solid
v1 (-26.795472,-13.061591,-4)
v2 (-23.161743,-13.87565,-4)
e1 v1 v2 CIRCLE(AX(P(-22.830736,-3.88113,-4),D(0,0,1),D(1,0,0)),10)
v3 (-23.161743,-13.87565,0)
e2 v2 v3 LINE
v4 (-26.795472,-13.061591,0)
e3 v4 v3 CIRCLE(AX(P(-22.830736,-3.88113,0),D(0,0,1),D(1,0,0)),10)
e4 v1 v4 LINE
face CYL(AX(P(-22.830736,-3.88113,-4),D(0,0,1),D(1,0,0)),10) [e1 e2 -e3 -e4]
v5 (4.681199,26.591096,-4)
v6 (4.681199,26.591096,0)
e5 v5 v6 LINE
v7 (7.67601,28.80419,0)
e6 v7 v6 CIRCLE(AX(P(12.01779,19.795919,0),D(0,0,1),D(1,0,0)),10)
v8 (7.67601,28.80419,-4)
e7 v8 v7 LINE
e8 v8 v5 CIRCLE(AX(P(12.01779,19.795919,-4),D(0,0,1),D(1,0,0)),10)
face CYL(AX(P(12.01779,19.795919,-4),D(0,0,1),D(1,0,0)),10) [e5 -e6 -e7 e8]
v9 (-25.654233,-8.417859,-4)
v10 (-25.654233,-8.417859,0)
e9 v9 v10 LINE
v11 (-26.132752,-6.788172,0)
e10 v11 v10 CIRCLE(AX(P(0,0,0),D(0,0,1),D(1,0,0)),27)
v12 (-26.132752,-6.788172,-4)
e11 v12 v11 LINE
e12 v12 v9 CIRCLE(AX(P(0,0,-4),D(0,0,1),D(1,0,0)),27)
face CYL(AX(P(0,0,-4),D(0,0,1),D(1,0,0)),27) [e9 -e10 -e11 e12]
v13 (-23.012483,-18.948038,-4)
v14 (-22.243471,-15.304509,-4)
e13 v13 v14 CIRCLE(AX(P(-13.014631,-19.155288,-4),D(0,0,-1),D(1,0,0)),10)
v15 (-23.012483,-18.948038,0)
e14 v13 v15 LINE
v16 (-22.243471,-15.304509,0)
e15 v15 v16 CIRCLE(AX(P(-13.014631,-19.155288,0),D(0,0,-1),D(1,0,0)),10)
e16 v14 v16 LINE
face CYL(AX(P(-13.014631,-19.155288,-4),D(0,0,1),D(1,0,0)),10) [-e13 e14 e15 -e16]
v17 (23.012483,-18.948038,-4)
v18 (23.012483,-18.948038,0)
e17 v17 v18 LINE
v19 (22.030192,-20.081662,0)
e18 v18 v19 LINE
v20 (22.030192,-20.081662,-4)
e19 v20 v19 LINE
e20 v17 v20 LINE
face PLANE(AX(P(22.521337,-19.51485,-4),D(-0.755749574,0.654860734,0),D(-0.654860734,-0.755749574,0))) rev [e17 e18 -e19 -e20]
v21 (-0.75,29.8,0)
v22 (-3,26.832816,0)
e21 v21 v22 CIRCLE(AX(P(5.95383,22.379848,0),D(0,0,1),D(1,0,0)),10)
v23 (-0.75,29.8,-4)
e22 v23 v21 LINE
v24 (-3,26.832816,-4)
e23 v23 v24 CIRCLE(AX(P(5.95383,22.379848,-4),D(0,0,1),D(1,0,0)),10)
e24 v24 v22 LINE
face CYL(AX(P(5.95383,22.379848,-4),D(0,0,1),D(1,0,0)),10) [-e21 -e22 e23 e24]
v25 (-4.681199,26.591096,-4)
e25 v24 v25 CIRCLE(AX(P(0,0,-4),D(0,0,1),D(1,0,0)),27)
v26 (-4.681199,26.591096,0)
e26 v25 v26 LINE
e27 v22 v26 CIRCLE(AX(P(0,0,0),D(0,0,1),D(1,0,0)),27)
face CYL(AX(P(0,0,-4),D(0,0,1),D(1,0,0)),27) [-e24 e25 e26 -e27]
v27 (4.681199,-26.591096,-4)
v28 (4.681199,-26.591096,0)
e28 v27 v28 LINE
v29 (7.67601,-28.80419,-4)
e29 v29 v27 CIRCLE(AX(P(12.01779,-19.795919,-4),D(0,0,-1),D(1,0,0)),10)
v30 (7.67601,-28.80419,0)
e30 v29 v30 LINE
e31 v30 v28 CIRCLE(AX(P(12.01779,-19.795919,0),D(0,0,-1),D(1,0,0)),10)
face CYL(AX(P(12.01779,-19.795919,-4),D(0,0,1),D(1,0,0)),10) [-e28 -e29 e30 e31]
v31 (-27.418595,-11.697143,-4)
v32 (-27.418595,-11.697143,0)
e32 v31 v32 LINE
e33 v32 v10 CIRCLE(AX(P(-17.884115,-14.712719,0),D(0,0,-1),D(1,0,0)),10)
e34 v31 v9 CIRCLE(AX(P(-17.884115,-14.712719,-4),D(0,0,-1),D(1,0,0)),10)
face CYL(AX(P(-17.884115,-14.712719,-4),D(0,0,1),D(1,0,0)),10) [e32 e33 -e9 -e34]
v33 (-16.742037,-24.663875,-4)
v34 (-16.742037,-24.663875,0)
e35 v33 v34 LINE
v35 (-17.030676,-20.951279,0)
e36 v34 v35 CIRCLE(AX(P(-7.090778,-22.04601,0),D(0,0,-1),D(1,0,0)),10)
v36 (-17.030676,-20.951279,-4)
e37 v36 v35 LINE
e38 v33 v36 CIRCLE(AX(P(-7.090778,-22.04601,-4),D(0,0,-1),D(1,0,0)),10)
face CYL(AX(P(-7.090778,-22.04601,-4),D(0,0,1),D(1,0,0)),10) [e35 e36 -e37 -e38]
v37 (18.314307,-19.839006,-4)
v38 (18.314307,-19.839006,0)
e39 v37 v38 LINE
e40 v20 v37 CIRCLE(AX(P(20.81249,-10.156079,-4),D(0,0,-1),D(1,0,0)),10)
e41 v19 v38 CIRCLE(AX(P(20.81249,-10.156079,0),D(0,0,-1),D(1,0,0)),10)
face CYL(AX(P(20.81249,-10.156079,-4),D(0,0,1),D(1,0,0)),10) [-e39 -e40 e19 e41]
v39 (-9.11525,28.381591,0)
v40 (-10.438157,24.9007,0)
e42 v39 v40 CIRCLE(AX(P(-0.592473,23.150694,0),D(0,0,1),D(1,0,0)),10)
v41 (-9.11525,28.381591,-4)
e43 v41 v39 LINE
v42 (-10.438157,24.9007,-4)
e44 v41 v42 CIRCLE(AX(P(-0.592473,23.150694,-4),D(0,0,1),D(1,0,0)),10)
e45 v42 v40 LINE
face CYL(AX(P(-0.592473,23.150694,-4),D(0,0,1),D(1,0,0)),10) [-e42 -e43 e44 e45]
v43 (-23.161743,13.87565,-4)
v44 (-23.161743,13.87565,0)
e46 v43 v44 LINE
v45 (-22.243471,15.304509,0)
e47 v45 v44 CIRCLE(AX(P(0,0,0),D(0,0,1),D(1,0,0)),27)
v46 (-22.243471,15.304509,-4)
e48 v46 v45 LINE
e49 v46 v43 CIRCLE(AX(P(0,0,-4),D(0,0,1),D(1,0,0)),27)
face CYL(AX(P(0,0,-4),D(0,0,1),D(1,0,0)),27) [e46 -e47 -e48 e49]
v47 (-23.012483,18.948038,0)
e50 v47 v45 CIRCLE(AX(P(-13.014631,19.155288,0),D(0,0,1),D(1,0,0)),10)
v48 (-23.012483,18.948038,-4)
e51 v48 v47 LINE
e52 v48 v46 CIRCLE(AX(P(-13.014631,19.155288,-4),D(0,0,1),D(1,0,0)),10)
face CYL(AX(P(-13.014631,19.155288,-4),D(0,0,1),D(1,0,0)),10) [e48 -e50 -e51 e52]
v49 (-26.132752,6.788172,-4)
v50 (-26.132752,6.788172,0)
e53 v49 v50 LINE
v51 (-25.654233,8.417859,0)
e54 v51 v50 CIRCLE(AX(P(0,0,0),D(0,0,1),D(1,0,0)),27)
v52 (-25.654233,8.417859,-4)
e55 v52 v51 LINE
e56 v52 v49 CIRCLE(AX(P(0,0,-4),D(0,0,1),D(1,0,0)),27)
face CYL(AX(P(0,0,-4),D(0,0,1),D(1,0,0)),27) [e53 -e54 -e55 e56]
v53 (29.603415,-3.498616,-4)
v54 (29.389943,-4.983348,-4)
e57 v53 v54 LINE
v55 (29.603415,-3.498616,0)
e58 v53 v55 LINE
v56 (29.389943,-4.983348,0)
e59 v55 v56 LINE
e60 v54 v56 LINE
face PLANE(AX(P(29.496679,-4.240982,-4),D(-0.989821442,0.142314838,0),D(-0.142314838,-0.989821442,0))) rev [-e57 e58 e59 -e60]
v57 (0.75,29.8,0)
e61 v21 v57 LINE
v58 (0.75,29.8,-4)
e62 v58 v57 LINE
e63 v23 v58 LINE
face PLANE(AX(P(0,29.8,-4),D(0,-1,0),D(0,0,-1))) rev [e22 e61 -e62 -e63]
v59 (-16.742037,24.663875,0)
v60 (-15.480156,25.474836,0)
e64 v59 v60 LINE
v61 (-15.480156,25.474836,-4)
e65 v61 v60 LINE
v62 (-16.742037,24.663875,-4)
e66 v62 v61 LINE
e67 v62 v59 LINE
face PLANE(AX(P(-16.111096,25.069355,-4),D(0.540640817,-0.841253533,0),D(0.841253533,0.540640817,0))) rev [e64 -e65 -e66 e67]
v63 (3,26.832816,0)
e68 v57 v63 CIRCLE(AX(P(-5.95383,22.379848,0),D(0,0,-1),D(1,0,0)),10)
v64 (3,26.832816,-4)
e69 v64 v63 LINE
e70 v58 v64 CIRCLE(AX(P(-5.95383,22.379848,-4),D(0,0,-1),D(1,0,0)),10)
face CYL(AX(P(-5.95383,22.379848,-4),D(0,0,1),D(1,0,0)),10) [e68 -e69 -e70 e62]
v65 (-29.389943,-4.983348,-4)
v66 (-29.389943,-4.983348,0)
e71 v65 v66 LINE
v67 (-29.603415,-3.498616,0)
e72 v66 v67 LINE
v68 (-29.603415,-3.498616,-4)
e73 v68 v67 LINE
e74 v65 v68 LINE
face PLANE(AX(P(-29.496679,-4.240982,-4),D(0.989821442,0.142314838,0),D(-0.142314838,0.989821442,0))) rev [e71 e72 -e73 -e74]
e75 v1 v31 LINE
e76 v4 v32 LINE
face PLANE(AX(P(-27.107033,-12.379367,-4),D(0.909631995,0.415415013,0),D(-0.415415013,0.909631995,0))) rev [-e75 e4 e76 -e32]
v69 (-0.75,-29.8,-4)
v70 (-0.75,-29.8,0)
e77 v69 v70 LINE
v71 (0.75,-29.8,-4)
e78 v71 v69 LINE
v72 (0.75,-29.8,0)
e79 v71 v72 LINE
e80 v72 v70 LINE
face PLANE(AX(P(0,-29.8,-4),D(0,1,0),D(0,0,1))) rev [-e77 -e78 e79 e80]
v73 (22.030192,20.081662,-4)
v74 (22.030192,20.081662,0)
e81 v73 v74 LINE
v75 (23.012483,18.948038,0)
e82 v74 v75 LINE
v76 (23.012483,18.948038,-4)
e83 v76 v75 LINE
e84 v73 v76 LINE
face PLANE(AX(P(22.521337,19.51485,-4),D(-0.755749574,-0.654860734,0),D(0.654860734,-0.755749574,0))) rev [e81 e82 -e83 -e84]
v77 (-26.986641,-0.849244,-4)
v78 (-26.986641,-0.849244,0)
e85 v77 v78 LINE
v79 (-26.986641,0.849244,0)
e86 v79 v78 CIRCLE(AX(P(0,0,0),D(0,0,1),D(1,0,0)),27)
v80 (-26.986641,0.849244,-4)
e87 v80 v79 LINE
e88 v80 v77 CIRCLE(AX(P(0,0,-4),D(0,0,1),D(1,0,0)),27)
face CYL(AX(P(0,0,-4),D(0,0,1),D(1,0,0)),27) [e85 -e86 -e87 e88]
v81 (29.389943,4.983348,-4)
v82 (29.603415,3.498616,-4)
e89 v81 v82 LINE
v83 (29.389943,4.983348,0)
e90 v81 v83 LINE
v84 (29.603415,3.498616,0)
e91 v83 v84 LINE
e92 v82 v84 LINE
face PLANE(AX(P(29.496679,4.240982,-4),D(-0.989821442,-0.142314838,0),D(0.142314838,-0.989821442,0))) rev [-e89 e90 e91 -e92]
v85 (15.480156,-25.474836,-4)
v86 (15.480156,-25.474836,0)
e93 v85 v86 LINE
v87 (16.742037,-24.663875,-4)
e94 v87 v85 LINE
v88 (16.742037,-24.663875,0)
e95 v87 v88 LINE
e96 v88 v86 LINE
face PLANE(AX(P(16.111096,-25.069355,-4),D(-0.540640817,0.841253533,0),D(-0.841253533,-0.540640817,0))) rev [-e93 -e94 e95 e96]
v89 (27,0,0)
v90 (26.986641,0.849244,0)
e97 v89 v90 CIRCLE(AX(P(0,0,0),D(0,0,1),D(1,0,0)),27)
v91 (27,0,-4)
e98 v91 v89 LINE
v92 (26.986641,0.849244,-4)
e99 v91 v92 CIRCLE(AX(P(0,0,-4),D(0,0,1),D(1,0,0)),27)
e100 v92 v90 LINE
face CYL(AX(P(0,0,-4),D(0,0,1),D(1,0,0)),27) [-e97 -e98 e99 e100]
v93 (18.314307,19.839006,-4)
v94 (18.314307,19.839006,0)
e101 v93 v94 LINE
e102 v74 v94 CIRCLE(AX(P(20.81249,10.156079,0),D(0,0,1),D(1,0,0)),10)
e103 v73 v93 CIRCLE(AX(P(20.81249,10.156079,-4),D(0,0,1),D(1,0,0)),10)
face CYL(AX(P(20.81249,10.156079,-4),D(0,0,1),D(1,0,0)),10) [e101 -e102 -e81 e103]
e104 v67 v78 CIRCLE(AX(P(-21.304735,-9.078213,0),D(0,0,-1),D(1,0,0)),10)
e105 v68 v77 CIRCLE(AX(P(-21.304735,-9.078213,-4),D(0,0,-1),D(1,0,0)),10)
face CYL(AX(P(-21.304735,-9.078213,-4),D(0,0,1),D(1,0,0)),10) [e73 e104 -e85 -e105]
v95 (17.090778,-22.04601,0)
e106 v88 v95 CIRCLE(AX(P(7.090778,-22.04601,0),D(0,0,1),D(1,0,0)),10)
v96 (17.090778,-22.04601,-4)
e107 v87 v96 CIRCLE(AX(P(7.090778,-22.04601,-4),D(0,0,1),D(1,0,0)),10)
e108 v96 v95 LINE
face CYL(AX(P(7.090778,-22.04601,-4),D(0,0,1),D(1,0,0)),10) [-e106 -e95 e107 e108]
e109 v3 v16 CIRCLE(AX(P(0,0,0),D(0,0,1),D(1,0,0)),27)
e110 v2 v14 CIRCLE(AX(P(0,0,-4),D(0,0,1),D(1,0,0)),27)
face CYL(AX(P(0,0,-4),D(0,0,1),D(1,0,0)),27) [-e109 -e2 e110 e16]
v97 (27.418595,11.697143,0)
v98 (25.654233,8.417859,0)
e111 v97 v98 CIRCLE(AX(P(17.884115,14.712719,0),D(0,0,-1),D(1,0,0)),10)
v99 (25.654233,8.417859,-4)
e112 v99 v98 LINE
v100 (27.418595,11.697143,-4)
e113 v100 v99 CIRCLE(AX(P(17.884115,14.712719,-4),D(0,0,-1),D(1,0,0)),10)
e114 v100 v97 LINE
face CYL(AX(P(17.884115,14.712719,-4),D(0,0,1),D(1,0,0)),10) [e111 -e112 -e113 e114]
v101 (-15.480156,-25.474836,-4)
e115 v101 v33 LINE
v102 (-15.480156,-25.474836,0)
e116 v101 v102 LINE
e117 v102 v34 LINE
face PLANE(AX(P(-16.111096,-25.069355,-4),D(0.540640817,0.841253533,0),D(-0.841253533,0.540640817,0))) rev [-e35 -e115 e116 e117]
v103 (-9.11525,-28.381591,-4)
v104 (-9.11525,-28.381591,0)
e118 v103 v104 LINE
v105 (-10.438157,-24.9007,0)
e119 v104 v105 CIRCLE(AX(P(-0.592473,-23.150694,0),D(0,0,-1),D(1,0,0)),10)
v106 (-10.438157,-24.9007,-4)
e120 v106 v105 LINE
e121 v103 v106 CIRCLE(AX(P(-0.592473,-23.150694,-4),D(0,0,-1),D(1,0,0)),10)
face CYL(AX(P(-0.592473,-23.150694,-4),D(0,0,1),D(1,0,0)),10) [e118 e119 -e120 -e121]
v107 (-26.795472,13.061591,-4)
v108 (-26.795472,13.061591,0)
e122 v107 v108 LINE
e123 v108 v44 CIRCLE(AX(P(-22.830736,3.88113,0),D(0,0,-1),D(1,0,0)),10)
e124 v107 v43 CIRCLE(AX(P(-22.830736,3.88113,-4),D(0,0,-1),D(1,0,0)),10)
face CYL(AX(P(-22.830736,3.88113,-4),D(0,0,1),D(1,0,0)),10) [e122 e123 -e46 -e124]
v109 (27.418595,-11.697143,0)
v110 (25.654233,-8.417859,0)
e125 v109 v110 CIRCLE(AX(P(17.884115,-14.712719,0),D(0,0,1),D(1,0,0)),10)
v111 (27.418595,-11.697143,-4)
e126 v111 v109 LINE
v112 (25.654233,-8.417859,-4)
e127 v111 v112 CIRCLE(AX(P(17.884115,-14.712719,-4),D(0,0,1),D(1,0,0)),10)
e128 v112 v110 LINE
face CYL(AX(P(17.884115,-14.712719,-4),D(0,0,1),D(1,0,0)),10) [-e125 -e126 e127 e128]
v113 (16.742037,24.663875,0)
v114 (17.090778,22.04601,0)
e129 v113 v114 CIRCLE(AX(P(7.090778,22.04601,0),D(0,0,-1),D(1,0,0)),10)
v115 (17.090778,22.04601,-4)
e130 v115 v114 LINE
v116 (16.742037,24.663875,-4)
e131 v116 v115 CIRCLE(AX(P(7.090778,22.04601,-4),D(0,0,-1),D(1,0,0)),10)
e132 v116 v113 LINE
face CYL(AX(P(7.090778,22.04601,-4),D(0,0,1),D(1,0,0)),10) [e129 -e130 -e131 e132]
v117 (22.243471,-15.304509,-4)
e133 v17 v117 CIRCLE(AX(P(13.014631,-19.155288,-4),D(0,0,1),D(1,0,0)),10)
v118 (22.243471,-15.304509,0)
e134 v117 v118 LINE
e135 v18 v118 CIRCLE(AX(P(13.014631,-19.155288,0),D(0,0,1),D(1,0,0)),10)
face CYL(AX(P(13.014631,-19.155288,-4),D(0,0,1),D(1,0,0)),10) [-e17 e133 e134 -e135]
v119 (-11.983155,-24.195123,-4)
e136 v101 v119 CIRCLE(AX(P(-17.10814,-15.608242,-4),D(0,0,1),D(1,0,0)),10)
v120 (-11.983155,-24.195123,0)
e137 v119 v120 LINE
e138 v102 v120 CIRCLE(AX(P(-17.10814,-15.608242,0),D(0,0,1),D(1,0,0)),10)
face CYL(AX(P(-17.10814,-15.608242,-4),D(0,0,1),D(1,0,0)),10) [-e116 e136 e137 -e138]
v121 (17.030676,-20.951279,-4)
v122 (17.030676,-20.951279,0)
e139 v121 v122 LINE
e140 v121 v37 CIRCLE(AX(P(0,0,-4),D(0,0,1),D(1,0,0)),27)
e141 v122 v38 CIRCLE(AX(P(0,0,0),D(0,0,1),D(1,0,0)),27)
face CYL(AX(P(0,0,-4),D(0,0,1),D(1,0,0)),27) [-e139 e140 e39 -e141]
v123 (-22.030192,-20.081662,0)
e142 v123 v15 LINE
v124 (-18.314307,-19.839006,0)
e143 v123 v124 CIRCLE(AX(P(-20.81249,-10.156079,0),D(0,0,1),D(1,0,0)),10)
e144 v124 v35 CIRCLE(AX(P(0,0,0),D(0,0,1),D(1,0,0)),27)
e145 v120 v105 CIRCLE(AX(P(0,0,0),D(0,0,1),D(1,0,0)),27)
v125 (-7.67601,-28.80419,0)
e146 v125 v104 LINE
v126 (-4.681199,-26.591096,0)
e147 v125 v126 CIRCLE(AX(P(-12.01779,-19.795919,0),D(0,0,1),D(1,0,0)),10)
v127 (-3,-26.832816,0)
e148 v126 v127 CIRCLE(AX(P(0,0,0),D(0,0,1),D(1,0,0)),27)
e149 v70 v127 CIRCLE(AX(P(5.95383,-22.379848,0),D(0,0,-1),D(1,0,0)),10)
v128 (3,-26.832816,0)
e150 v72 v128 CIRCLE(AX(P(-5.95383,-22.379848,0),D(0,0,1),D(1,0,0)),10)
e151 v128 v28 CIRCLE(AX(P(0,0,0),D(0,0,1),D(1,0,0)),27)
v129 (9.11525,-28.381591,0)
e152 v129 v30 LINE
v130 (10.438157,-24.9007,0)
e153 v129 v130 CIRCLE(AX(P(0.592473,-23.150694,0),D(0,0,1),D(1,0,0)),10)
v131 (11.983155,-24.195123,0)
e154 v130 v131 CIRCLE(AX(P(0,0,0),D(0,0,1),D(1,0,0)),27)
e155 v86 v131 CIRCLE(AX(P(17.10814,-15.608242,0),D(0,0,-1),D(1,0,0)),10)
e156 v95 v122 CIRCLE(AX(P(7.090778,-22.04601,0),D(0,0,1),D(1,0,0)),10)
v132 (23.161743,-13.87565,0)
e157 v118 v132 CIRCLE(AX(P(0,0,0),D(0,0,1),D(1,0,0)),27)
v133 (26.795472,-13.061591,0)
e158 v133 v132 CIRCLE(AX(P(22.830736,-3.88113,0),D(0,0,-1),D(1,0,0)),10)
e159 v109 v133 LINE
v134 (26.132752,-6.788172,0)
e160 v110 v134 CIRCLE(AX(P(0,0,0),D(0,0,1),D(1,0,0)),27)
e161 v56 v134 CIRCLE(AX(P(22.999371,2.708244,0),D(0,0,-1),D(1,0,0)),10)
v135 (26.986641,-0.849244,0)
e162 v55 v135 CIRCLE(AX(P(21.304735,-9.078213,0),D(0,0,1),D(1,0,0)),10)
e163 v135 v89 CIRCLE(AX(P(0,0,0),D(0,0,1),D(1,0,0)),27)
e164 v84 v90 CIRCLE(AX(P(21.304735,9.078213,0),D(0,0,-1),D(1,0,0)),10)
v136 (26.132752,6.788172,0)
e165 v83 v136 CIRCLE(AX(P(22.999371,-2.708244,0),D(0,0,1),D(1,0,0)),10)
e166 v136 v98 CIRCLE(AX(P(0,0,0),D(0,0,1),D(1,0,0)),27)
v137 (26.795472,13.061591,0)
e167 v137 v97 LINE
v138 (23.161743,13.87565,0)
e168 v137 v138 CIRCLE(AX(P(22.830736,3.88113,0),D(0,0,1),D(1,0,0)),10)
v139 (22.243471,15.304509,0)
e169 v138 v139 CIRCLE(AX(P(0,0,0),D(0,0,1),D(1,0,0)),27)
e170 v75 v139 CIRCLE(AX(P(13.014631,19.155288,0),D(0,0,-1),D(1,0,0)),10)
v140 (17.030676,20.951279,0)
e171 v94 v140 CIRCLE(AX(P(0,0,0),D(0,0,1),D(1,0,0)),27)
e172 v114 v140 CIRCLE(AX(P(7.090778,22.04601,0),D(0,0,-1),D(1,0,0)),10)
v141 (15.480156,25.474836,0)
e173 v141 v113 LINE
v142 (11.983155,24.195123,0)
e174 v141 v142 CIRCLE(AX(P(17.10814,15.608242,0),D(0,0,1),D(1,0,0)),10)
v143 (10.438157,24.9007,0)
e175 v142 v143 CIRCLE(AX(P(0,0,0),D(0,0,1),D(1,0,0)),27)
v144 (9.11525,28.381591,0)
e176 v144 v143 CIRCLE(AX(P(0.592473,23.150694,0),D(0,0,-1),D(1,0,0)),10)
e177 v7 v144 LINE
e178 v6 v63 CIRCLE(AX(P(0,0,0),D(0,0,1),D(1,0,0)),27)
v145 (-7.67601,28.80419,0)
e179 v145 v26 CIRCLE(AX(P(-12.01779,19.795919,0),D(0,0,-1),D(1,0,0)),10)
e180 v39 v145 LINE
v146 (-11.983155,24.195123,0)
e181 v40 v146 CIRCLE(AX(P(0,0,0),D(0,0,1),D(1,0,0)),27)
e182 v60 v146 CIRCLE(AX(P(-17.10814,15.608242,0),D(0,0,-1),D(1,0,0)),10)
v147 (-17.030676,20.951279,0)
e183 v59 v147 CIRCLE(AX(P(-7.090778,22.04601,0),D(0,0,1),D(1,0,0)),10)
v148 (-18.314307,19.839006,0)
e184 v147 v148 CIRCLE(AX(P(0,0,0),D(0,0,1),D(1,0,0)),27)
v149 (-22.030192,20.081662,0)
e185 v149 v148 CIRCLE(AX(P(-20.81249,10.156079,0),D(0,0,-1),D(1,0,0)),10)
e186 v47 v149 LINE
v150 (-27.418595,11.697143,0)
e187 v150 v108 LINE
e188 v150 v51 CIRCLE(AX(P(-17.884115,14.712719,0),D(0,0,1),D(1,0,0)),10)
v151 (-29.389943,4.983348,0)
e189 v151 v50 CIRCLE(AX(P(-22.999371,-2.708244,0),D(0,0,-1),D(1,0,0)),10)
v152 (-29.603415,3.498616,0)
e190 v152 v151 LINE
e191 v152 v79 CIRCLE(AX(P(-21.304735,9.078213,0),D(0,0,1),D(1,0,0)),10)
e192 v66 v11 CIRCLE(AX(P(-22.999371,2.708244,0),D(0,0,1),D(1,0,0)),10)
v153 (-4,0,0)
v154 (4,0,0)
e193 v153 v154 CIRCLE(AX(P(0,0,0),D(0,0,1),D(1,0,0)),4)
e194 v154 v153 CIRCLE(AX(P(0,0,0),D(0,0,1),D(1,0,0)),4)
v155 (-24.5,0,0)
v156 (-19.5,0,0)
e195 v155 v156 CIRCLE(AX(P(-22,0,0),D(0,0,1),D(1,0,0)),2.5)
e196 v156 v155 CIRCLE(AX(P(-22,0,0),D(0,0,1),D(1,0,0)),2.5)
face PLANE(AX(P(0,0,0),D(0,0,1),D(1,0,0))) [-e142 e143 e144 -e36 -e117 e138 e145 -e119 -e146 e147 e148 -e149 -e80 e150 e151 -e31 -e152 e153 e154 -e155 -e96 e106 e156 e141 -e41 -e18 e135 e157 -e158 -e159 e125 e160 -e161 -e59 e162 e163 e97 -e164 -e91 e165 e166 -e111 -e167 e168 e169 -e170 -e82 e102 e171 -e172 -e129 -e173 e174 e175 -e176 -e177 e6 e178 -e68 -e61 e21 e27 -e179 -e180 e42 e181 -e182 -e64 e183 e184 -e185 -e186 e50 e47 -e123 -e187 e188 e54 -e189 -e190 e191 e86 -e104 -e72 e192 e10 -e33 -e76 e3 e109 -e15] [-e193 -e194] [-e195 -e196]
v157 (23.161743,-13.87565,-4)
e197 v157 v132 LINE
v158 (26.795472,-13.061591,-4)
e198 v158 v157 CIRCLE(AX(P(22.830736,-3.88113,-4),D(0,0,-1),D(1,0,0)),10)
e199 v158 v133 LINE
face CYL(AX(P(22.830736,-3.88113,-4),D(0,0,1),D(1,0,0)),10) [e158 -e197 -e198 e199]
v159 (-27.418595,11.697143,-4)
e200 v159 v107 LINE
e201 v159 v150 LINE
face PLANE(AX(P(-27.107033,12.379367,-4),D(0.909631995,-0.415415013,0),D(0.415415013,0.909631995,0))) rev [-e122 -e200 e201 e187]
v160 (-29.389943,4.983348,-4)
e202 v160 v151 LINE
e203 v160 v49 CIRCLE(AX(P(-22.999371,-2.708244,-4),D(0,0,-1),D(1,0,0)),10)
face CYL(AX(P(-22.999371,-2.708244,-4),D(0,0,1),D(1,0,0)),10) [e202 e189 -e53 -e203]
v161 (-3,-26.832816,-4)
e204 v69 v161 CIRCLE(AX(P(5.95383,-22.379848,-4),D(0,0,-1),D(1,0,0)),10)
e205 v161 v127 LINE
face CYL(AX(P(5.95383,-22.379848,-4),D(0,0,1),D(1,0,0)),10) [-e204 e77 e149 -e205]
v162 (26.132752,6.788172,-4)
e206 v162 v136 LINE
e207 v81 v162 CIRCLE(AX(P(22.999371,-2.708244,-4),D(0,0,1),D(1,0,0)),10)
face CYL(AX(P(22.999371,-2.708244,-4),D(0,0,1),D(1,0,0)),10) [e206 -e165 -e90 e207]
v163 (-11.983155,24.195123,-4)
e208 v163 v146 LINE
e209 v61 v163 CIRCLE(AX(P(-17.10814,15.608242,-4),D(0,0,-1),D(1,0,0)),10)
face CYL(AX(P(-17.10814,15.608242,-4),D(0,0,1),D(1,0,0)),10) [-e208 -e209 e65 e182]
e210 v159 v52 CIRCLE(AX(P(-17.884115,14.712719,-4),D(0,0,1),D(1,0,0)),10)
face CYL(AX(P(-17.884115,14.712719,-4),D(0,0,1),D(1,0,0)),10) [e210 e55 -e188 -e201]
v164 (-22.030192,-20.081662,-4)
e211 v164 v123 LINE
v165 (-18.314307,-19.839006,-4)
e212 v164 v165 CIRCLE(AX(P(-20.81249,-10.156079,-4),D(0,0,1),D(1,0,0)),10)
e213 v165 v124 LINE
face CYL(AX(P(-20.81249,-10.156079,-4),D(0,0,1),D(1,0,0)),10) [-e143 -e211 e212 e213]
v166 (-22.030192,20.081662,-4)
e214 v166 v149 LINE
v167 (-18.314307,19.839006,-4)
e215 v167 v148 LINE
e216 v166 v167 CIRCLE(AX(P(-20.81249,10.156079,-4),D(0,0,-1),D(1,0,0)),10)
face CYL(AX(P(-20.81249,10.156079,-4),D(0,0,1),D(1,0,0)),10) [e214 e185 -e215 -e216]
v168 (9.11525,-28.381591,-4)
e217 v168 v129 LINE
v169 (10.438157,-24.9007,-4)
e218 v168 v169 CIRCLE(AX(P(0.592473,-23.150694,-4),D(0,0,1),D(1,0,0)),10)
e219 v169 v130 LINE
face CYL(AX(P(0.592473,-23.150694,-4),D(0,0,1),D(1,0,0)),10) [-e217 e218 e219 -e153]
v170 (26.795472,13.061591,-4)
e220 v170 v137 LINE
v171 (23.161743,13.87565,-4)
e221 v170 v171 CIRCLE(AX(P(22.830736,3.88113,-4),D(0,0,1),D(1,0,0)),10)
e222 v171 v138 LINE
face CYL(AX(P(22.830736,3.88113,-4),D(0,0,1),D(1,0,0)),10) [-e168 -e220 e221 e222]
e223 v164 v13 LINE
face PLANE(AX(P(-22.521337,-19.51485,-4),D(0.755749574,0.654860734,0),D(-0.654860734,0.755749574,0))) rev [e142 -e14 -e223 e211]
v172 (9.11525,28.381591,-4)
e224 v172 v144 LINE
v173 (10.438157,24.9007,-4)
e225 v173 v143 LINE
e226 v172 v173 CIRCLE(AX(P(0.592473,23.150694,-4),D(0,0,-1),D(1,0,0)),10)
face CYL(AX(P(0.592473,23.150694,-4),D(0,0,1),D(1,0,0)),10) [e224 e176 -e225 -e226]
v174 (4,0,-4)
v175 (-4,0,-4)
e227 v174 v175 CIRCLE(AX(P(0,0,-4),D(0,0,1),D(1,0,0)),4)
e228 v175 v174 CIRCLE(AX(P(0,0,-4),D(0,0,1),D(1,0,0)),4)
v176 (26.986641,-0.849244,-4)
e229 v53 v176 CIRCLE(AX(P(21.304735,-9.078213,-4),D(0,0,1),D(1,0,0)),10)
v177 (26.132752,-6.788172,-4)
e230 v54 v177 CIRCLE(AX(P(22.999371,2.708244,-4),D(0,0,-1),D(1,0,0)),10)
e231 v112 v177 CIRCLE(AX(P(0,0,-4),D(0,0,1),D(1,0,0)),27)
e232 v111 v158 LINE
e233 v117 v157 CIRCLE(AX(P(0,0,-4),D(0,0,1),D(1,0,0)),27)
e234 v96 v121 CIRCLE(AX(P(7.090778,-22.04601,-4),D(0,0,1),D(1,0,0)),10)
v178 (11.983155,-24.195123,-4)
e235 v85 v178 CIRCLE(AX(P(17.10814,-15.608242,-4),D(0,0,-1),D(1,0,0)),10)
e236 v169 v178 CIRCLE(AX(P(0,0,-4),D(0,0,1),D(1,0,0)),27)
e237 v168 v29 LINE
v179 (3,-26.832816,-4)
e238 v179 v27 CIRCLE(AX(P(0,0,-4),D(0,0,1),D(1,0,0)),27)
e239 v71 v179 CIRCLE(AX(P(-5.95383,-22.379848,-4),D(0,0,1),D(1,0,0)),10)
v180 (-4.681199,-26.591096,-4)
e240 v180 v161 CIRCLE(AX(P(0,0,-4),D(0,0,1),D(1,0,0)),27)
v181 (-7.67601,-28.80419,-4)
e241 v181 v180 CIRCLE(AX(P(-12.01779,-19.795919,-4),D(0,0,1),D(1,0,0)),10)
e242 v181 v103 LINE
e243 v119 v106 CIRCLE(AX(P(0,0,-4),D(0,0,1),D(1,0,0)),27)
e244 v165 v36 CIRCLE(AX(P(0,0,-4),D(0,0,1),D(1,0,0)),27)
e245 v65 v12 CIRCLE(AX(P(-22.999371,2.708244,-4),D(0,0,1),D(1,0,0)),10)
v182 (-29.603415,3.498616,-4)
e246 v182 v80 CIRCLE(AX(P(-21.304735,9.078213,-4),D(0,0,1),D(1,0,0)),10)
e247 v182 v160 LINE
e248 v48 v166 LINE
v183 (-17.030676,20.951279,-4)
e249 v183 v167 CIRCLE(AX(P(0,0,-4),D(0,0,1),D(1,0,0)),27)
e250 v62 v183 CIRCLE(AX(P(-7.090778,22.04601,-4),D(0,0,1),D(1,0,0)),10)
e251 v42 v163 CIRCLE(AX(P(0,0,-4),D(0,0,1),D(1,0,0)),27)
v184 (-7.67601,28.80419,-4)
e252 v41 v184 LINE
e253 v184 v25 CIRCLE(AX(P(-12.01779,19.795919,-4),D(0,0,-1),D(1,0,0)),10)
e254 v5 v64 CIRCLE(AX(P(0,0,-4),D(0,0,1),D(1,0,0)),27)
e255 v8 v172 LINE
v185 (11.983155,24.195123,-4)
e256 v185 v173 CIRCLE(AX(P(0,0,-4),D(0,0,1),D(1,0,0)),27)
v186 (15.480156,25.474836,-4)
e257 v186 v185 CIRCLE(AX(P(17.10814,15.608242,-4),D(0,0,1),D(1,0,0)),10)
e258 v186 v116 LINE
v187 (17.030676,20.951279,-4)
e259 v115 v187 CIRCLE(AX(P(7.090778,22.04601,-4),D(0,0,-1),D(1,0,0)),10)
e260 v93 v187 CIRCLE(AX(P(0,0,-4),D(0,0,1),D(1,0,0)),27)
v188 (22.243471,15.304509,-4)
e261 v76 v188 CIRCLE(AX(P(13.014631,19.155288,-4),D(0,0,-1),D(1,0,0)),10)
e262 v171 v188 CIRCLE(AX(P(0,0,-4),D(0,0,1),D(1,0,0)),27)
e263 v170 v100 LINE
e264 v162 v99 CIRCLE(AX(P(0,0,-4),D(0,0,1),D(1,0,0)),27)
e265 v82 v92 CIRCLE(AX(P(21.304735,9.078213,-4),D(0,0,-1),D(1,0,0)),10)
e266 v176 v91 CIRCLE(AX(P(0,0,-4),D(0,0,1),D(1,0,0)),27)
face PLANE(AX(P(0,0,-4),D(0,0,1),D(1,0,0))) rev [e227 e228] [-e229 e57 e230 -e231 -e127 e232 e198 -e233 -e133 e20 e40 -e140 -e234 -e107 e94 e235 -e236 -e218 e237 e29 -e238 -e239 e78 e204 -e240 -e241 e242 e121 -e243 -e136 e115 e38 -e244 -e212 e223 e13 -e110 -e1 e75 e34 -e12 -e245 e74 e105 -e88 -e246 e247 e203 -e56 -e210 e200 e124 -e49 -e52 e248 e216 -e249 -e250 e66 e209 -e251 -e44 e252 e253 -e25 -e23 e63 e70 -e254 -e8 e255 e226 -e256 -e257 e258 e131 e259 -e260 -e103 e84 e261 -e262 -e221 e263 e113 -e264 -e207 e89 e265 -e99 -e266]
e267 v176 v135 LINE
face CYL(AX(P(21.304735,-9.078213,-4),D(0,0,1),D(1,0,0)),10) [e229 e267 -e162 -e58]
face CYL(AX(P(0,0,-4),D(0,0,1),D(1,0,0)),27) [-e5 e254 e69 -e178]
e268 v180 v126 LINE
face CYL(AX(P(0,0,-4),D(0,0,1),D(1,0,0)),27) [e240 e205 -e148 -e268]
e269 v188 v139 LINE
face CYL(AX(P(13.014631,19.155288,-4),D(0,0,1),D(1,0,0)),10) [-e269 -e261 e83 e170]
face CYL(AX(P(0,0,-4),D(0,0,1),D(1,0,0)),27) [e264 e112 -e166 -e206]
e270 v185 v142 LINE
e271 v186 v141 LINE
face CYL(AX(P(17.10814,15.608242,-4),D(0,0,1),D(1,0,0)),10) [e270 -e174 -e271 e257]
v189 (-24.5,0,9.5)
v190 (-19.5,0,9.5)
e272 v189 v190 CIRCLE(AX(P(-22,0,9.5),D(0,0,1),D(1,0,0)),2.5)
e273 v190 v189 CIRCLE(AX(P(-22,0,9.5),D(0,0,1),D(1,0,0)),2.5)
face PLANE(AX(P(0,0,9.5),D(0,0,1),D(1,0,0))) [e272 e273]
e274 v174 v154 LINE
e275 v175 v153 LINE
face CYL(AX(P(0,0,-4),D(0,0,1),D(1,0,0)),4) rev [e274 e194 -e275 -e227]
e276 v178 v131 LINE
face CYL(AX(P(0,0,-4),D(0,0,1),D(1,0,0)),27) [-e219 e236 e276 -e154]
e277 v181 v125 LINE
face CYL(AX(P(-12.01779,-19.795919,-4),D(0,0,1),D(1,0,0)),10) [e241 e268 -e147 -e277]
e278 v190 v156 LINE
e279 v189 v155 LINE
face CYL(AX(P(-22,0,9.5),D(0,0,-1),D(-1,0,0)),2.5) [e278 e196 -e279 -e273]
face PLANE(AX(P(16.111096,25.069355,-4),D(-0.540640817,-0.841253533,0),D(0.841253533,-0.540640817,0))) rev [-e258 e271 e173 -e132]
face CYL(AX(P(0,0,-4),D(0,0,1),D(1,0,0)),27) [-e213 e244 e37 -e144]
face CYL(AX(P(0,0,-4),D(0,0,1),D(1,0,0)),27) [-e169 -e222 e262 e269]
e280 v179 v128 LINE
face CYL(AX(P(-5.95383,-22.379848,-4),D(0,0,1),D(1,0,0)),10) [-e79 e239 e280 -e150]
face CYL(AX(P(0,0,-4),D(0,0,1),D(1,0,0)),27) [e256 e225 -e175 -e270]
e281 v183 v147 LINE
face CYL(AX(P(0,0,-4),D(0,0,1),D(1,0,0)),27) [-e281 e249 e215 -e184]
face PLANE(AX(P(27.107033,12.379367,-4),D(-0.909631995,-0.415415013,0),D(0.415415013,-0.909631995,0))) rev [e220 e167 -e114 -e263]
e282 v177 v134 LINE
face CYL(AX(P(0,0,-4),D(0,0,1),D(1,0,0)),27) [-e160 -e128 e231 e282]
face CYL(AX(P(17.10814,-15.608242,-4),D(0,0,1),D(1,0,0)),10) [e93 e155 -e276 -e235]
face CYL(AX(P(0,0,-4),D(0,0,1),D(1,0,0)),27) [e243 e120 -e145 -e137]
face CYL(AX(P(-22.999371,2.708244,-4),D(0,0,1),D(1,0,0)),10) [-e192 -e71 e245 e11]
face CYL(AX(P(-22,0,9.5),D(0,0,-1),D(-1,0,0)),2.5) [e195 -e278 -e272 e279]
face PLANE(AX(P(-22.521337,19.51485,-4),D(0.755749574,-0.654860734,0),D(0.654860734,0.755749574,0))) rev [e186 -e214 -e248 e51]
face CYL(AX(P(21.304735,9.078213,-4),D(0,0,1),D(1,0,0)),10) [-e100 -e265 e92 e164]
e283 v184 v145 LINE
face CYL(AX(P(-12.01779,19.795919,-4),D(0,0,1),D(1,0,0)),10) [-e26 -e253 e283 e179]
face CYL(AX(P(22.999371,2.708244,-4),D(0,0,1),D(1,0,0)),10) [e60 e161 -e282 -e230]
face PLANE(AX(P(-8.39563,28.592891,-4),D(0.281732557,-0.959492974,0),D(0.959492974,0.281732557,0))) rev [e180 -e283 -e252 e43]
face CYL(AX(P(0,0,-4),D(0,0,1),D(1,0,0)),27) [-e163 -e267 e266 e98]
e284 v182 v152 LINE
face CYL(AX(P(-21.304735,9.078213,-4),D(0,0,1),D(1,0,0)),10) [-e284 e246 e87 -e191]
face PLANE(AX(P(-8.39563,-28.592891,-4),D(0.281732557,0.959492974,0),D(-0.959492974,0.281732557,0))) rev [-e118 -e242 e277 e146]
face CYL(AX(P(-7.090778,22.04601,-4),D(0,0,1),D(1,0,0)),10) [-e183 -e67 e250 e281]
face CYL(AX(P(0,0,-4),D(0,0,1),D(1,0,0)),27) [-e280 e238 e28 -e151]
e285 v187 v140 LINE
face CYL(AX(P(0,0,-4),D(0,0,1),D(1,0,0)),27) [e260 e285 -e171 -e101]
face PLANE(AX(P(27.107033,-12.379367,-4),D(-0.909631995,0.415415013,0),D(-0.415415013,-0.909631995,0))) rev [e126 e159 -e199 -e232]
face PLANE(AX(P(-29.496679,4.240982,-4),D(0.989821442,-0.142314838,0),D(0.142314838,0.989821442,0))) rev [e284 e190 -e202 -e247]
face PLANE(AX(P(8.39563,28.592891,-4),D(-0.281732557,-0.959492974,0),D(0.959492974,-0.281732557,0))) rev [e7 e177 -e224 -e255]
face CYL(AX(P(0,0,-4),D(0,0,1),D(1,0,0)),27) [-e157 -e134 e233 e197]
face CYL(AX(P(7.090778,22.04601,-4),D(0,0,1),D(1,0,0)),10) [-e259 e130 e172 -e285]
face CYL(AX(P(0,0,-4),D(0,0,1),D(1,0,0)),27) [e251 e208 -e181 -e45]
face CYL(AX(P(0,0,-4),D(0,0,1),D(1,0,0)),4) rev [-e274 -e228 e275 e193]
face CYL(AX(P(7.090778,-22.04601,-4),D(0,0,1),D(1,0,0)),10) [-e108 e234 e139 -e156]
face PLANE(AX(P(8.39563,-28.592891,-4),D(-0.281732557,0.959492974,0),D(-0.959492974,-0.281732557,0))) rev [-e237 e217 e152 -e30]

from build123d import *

# Parameters (mm, degrees)
GEAR_PROFILE_SKETCH_R = 4
GEAR_BODY_22T_DEPTH   = 4
SKETCH1_3_R           = 2.5
HUB_BOSS_DEPTH        = 9.5


with BuildPart() as part:
    # Gear Profile Sketch → Gear Body 22T (new body)
    with BuildSketch(Plane.XY):
        with BuildLine():
            Line((-0.75, 29.8), (0.75, 29.8))
            ThreePointArc((0.75, 29.8), (2.014333197, 28.422063485), (3, 26.83281573))
            ThreePointArc((3, 26.83281573), (3.842500633, 26.725178931), (4.681198862, 26.591095826))
            ThreePointArc((4.681198862, 26.591095826), (6.074682067, 27.838273451), (7.676010464, 28.804190031))
            Line((7.676010464, 28.804190031), (9.115249924, 28.381591196))
            ThreePointArc((9.115249924, 28.381591196), (9.940159165, 26.703266967), (10.438156704, 24.900700485))
            ThreePointArc((10.438156704, 24.900700485), (11.216205351, 24.560063875), (11.983154832, 24.195123481))
            ThreePointArc((11.983154832, 24.195123481), (13.671562718, 24.999192063), (15.480156211, 25.474835891))
            Line((15.480156211, 25.474835891), (16.74203651, 24.663874665))
            ThreePointArc((16.74203651, 24.663874665), (17.060692554, 22.821130571), (17.030676029, 20.951278576))
            ThreePointArc((17.030676029, 20.951278576), (17.681239817, 20.405238508), (18.314306865, 19.839006126))
            ThreePointArc((18.314306865, 19.839006126), (20.160854665, 20.13482481), (22.030191765, 20.081662052))
            Line((22.030191765, 20.081662052), (23.012482866, 18.948037691))
            ThreePointArc((23.012482866, 18.948037691), (22.799070097, 17.090161898), (22.243471269, 15.30450868))
            ThreePointArc((22.243471269, 15.30450868), (22.713845386, 14.597302071), (23.161742674, 13.875650481))
            ThreePointArc((23.161742674, 13.875650481), (25.016834069, 13.639253797), (26.795472202, 13.061591384))
            Line((26.795472202, 13.061591384), (27.418594721, 11.697143391))
            ThreePointArc((27.418594721, 11.697143391), (26.690402571, 9.974649947), (25.654232752, 8.417858509))
            ThreePointArc((25.654232752, 8.417858509), (25.906310288, 7.606779035), (26.132751841, 6.788172157))
            ThreePointArc((26.132751841, 6.788172157), (27.846098357, 6.038711558), (29.389942839, 4.983348262))
            Line((29.389942839, 4.983348262), (29.603415097, 3.498616099))
            ThreePointArc((29.603415097, 3.498616099), (28.419437363, 2.051051179), (26.98664087, 0.849243505))
            ThreePointArc((26.98664087, 0.849243505), (27, 0), (26.98664087, -0.849243505))
            ThreePointArc((26.98664087, -0.849243505), (28.419437363, -2.051051179), (29.603415097, -3.498616099))
            Line((29.603415097, -3.498616099), (29.389942839, -4.983348262))
            ThreePointArc((29.389942839, -4.983348262), (27.846098357, -6.038711558), (26.132751841, -6.788172157))
            ThreePointArc((26.132751841, -6.788172157), (25.906310288, -7.606779035), (25.654232752, -8.417858509))
            ThreePointArc((25.654232752, -8.417858509), (26.690402571, -9.974649947), (27.418594721, -11.697143391))
            Line((27.418594721, -11.697143391), (26.795472202, -13.061591384))
            ThreePointArc((26.795472202, -13.061591384), (25.016834069, -13.639253797), (23.161742674, -13.875650481))
            ThreePointArc((23.161742674, -13.875650481), (22.713845386, -14.597302071), (22.243471269, -15.30450868))
            ThreePointArc((22.243471269, -15.30450868), (22.799070097, -17.090161898), (23.012482866, -18.948037691))
            Line((23.012482866, -18.948037691), (22.030191765, -20.081662052))
            ThreePointArc((22.030191765, -20.081662052), (20.160854665, -20.13482481), (18.314306865, -19.839006126))
            ThreePointArc((18.314306865, -19.839006126), (17.681239817, -20.405238508), (17.030676029, -20.951278576))
            ThreePointArc((17.030676029, -20.951278576), (17.060692554, -22.821130571), (16.74203651, -24.663874665))
            Line((16.74203651, -24.663874665), (15.480156211, -25.474835891))
            ThreePointArc((15.480156211, -25.474835891), (13.671562718, -24.999192063), (11.983154832, -24.195123481))
            ThreePointArc((11.983154832, -24.195123481), (11.216205351, -24.560063875), (10.438156704, -24.900700485))
            ThreePointArc((10.438156704, -24.900700485), (9.940159165, -26.703266967), (9.115249924, -28.381591196))
            Line((9.115249924, -28.381591196), (7.676010464, -28.804190031))
            ThreePointArc((7.676010464, -28.804190031), (6.074682067, -27.838273451), (4.681198862, -26.591095826))
            ThreePointArc((4.681198862, -26.591095826), (3.842500633, -26.725178931), (3, -26.83281573))
            ThreePointArc((3, -26.83281573), (2.014333197, -28.422063485), (0.75, -29.8))
            Line((0.75, -29.8), (-0.75, -29.8))
            ThreePointArc((-0.75, -29.8), (-2.014333197, -28.422063485), (-3, -26.83281573))
            ThreePointArc((-3, -26.83281573), (-3.842500633, -26.725178931), (-4.681198862, -26.591095826))
            ThreePointArc((-4.681198862, -26.591095826), (-6.074682067, -27.838273451), (-7.676010464, -28.804190031))
            Line((-7.676010464, -28.804190031), (-9.115249924, -28.381591196))
            ThreePointArc((-9.115249924, -28.381591196), (-9.940159165, -26.703266967), (-10.438156704, -24.900700485))
            ThreePointArc((-10.438156704, -24.900700485), (-11.216205351, -24.560063875), (-11.983154832, -24.195123481))
            ThreePointArc((-11.983154832, -24.195123481), (-13.671562718, -24.999192063), (-15.480156211, -25.474835891))
            Line((-15.480156211, -25.474835891), (-16.74203651, -24.663874665))
            ThreePointArc((-16.74203651, -24.663874665), (-17.060692554, -22.821130571), (-17.030676029, -20.951278576))
            ThreePointArc((-17.030676029, -20.951278576), (-17.681239817, -20.405238508), (-18.314306865, -19.839006126))
            ThreePointArc((-18.314306865, -19.839006126), (-20.160854665, -20.13482481), (-22.030191765, -20.081662052))
            Line((-22.030191765, -20.081662052), (-23.012482866, -18.948037691))
            ThreePointArc((-23.012482866, -18.948037691), (-22.799070097, -17.090161898), (-22.243471269, -15.30450868))
            ThreePointArc((-22.243471269, -15.30450868), (-22.713845386, -14.597302071), (-23.161742674, -13.875650481))
            ThreePointArc((-23.161742674, -13.875650481), (-25.016834069, -13.639253797), (-26.795472202, -13.061591384))
            Line((-26.795472202, -13.061591384), (-27.418594721, -11.697143391))
            ThreePointArc((-27.418594721, -11.697143391), (-26.690402571, -9.974649947), (-25.654232752, -8.417858509))
            ThreePointArc((-25.654232752, -8.417858509), (-25.906310288, -7.606779035), (-26.132751841, -6.788172157))
            ThreePointArc((-26.132751841, -6.788172157), (-27.846098357, -6.038711558), (-29.389942839, -4.983348262))
            Line((-29.389942839, -4.983348262), (-29.603415097, -3.498616099))
            ThreePointArc((-29.603415097, -3.498616099), (-28.419437363, -2.051051179), (-26.98664087, -0.849243505))
            ThreePointArc((-26.98664087, -0.849243505), (-27, 0), (-26.98664087, 0.849243505))
            ThreePointArc((-26.98664087, 0.849243505), (-28.419437363, 2.051051179), (-29.603415097, 3.498616099))
            Line((-29.603415097, 3.498616099), (-29.389942839, 4.983348262))
            ThreePointArc((-29.389942839, 4.983348262), (-27.846098357, 6.038711558), (-26.132751841, 6.788172157))
            ThreePointArc((-26.132751841, 6.788172157), (-25.906310288, 7.606779035), (-25.654232752, 8.417858509))
            ThreePointArc((-25.654232752, 8.417858509), (-26.690402571, 9.974649947), (-27.418594721, 11.697143391))
            Line((-27.418594721, 11.697143391), (-26.795472202, 13.061591384))
            ThreePointArc((-26.795472202, 13.061591384), (-25.016834069, 13.639253797), (-23.161742674, 13.875650481))
            ThreePointArc((-23.161742674, 13.875650481), (-22.713845386, 14.597302071), (-22.243471269, 15.30450868))
            ThreePointArc((-22.243471269, 15.30450868), (-22.799070097, 17.090161898), (-23.012482866, 18.948037691))
            Line((-23.012482866, 18.948037691), (-22.030191765, 20.081662052))
            ThreePointArc((-22.030191765, 20.081662052), (-20.160854665, 20.13482481), (-18.314306865, 19.839006126))
            ThreePointArc((-18.314306865, 19.839006126), (-17.681239817, 20.405238508), (-17.030676029, 20.951278576))
            ThreePointArc((-17.030676029, 20.951278576), (-17.060692554, 22.821130571), (-16.74203651, 24.663874665))
            Line((-16.74203651, 24.663874665), (-15.480156211, 25.474835891))
            ThreePointArc((-15.480156211, 25.474835891), (-13.671562718, 24.999192063), (-11.983154832, 24.195123481))
            ThreePointArc((-11.983154832, 24.195123481), (-11.216205351, 24.560063875), (-10.438156704, 24.900700485))
            ThreePointArc((-10.438156704, 24.900700485), (-9.940159165, 26.703266967), (-9.115249924, 28.381591196))
            Line((-9.115249924, 28.381591196), (-7.676010464, 28.804190031))
            ThreePointArc((-7.676010464, 28.804190031), (-6.074682067, 27.838273451), (-4.681198862, 26.591095826))
            ThreePointArc((-4.681198862, 26.591095826), (-3.842500633, 26.725178931), (-3, 26.83281573))
            ThreePointArc((-3, 26.83281573), (-2.014333197, 28.422063485), (-0.75, 29.8))
        make_face()
        Circle(GEAR_PROFILE_SKETCH_R, mode=Mode.SUBTRACT)
    extrude(amount=-GEAR_BODY_22T_DEPTH)

    # Sketch1_3 → Hub Boss (add)
    with BuildSketch(Plane.XY):
        with Locations((-22, 0)):
            Circle(SKETCH1_3_R)
    extrude(amount=HUB_BOSS_DEPTH)


solid = part.part
